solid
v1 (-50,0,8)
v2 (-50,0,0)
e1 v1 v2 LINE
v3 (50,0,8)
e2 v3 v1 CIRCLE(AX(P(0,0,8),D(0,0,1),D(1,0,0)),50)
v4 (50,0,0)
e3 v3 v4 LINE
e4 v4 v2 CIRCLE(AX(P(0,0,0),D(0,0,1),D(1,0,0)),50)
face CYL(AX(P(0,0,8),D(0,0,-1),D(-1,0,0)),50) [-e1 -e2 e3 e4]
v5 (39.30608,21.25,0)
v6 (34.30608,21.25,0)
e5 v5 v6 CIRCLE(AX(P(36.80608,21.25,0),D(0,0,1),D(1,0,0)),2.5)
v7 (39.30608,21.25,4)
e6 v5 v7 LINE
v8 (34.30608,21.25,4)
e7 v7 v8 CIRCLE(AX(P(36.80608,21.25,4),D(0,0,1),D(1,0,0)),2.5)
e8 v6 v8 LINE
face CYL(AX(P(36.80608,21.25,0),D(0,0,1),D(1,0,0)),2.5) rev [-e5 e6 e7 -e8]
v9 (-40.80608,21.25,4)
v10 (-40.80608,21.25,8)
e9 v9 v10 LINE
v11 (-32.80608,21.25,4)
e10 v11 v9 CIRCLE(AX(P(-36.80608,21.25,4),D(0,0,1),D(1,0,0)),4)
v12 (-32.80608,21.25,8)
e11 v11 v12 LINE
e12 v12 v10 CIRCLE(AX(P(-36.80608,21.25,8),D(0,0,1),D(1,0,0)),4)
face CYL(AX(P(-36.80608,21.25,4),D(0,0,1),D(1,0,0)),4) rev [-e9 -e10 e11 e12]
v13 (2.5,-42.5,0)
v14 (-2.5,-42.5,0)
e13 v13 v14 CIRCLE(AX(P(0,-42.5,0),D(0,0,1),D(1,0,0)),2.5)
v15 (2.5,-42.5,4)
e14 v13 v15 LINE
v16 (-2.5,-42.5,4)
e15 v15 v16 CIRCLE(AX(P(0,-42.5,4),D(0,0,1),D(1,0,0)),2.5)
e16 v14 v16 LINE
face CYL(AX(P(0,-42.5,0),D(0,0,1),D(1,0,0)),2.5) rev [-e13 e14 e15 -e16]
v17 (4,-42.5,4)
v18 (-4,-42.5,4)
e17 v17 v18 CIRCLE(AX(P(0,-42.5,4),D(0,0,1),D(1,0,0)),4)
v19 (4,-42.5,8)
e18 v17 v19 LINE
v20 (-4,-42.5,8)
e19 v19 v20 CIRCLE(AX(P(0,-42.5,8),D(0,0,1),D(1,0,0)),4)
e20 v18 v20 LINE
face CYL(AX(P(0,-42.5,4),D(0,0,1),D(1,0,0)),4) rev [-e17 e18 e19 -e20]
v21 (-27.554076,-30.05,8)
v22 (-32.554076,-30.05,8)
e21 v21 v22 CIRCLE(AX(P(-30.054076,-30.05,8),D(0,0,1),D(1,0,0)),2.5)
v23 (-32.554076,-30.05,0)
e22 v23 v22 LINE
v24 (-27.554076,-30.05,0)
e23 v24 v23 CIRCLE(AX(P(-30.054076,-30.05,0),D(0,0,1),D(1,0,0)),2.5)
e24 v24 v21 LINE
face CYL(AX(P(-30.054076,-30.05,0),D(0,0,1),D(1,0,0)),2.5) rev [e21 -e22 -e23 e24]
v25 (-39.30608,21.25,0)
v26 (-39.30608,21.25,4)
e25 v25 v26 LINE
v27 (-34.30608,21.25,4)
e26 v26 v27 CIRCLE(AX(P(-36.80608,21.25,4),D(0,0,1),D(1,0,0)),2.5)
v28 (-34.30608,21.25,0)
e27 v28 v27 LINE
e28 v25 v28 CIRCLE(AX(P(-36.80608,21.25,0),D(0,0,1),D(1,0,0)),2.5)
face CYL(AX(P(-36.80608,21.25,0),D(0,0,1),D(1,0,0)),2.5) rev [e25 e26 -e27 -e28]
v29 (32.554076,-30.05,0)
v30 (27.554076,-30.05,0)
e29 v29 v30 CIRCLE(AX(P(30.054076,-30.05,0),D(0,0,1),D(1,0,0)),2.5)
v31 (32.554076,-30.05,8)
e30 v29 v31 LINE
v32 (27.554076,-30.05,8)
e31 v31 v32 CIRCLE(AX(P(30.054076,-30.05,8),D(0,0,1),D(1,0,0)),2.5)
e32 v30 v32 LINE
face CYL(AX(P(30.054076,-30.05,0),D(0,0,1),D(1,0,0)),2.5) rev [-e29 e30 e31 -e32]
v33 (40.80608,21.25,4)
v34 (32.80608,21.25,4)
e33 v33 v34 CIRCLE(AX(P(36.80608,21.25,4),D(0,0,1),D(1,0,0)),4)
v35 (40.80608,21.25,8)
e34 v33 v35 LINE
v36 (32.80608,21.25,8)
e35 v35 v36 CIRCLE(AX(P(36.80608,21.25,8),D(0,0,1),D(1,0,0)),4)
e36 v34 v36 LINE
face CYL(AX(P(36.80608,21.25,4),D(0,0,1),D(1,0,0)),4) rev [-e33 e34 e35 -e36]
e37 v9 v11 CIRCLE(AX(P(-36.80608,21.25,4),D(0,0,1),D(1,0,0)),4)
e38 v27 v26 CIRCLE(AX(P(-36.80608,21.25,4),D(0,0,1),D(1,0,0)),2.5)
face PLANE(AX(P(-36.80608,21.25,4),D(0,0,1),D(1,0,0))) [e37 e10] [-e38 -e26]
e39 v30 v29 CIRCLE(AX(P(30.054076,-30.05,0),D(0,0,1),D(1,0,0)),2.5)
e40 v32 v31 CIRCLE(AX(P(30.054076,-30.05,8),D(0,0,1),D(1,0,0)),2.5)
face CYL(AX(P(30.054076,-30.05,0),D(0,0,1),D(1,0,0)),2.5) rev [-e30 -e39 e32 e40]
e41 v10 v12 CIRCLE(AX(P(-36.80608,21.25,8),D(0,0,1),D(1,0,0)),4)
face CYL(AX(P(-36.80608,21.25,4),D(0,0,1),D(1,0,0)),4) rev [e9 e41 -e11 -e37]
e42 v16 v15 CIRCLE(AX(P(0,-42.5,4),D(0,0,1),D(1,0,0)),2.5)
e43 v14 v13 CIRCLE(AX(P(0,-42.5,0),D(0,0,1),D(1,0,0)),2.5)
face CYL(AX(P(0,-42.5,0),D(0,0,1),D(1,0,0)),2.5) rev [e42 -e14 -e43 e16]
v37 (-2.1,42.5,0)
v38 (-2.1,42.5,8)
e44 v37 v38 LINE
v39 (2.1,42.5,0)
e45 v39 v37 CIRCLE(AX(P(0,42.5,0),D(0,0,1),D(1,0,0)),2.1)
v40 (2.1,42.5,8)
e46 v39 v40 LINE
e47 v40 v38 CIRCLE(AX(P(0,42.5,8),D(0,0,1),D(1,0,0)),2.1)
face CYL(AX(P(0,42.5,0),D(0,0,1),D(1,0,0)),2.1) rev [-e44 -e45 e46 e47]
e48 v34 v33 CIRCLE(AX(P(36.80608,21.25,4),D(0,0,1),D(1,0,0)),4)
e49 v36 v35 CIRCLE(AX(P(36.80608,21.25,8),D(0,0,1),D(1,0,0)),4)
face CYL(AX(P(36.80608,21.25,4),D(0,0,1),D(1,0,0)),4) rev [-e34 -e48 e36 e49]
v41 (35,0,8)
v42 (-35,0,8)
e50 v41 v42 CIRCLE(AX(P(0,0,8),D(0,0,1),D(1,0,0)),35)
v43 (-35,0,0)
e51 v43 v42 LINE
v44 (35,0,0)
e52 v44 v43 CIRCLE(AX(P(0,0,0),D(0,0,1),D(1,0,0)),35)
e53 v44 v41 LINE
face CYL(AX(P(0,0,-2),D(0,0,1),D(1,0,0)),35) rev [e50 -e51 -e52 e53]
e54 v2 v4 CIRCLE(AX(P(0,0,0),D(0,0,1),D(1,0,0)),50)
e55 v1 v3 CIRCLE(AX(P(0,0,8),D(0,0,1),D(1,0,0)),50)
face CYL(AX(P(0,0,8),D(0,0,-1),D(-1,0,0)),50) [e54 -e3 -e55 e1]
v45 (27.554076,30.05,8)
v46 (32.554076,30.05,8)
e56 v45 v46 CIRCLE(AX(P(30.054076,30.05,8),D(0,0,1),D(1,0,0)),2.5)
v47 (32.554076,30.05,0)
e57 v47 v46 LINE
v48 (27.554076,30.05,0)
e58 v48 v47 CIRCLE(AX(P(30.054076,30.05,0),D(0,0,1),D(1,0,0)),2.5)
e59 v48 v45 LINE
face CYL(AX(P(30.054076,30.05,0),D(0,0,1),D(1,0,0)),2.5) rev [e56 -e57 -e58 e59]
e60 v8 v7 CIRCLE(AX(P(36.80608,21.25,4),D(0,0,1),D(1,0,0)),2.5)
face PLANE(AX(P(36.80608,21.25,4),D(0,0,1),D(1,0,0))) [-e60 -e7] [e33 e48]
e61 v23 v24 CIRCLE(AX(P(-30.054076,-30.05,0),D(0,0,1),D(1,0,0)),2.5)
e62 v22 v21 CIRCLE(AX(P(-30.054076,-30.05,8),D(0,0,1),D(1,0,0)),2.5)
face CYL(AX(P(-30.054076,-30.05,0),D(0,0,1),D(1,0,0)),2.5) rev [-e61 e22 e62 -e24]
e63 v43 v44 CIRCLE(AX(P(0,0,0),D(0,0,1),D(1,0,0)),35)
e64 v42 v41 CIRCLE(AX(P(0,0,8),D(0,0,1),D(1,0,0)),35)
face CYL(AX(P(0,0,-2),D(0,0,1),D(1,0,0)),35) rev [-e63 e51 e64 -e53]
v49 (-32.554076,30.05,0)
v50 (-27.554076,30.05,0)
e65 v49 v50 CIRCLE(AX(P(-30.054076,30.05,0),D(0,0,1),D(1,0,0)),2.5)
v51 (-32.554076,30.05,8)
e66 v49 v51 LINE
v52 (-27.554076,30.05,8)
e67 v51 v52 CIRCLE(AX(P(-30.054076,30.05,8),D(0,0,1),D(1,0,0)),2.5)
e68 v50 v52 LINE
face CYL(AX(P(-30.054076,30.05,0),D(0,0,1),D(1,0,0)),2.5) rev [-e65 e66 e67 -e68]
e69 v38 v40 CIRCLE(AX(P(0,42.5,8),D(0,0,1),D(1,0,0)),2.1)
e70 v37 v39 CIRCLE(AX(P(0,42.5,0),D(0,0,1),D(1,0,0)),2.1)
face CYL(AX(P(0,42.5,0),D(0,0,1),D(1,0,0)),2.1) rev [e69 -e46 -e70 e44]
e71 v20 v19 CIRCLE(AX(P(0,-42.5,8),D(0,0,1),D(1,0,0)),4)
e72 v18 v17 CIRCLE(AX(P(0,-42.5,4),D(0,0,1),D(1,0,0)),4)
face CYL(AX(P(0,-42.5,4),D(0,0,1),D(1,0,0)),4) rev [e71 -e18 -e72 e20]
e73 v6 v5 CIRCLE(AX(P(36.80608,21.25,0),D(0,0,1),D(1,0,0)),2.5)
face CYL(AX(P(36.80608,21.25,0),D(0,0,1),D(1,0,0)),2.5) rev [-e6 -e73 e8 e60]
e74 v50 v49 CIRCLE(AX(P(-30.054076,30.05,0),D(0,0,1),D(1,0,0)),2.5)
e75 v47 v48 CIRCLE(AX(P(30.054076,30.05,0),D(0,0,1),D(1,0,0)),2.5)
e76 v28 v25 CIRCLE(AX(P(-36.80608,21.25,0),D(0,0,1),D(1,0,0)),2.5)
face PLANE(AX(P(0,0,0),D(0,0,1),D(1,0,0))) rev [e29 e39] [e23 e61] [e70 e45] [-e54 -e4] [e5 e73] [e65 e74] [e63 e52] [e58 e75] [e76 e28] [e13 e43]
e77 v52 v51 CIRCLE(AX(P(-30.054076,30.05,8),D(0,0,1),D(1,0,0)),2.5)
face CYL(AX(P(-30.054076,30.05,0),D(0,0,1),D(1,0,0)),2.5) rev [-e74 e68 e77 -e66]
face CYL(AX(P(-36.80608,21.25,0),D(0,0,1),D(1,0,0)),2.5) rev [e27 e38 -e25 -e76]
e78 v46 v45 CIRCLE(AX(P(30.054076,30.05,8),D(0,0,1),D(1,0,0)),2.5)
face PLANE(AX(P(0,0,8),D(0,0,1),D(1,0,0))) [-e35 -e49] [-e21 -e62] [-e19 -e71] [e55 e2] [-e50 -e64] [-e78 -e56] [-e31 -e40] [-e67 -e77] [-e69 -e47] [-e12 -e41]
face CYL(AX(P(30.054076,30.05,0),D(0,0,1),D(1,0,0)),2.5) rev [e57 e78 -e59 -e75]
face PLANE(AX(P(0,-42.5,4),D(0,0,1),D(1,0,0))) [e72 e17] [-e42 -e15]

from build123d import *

# Parameters (mm, degrees)
SKETCH1_R           = 50
BOSS_EXTRUDE1_DEPTH = 8
SKETCH2_R           = 2.5
CUT_EXTRUDE1_DEPTH  = 8
SKETCH3_R           = 2.1
CUT_EXTRUDE2_DEPTH  = 8
SKETCH4_R           = 4
CUT_EXTRUDE3_DEPTH  = 4
SKETCH5_R           = 2.5
CUT_EXTRUDE4_DEPTH  = 4
SKETCH6_R           = 35
CUT_EXTRUDE5_DEPTH  = 10


with BuildPart() as part:
    # Sketch1 → Boss-Extrude1 (new body)
    with BuildSketch(Plane.XY):
        Circle(SKETCH1_R)
    extrude(amount=BOSS_EXTRUDE1_DEPTH)

    # Sketch2 → Cut-Extrude1 (cut)
    with BuildSketch(Plane.XY.offset(8)):
        with Locations((-30.054076263, 30.05)):
            Circle(SKETCH2_R)
        with Locations((30.054076263, 30.05)):
            Circle(SKETCH2_R)
        with Locations((-30.054076263, -30.05)):
            Circle(SKETCH2_R)
        with Locations((30.054076263, -30.05)):
            Circle(SKETCH2_R)
    extrude(amount=-CUT_EXTRUDE1_DEPTH, mode=Mode.SUBTRACT)

    # Sketch3 → Cut-Extrude2 (cut)
    with BuildSketch(Plane.XY.offset(8)):
        with Locations((0, 42.5)):
            Circle(SKETCH3_R)
    extrude(amount=-CUT_EXTRUDE2_DEPTH, mode=Mode.SUBTRACT)

    # Sketch4 → Cut-Extrude3 (cut)
    with BuildSketch(Plane.XY.offset(8)):
        with Locations((0, -42.5)):
            Circle(SKETCH4_R)
        with Locations((-36.806079661, 21.25)):
            Circle(SKETCH4_R)
        with Locations((36.806079661, 21.25)):
            Circle(SKETCH4_R)
    extrude(amount=-CUT_EXTRUDE3_DEPTH, mode=Mode.SUBTRACT)

    # Sketch5 → Cut-Extrude4 (cut)
    with BuildSketch(Plane.XY.offset(4)):
        with Locations((-36.806079661, 21.25)):
            Circle(SKETCH5_R)
        with Locations((0, -42.5)):
            Circle(SKETCH5_R)
        with Locations((36.806079661, 21.25)):
            Circle(SKETCH5_R)
    extrude(amount=-CUT_EXTRUDE4_DEPTH, mode=Mode.SUBTRACT)

    # Sketch6 → Cut-Extrude5 (cut)
    with BuildSketch(Plane.XY.offset(8)):
        Circle(SKETCH6_R)
    extrude(amount=-CUT_EXTRUDE5_DEPTH, mode=Mode.SUBTRACT)


solid = part.part
